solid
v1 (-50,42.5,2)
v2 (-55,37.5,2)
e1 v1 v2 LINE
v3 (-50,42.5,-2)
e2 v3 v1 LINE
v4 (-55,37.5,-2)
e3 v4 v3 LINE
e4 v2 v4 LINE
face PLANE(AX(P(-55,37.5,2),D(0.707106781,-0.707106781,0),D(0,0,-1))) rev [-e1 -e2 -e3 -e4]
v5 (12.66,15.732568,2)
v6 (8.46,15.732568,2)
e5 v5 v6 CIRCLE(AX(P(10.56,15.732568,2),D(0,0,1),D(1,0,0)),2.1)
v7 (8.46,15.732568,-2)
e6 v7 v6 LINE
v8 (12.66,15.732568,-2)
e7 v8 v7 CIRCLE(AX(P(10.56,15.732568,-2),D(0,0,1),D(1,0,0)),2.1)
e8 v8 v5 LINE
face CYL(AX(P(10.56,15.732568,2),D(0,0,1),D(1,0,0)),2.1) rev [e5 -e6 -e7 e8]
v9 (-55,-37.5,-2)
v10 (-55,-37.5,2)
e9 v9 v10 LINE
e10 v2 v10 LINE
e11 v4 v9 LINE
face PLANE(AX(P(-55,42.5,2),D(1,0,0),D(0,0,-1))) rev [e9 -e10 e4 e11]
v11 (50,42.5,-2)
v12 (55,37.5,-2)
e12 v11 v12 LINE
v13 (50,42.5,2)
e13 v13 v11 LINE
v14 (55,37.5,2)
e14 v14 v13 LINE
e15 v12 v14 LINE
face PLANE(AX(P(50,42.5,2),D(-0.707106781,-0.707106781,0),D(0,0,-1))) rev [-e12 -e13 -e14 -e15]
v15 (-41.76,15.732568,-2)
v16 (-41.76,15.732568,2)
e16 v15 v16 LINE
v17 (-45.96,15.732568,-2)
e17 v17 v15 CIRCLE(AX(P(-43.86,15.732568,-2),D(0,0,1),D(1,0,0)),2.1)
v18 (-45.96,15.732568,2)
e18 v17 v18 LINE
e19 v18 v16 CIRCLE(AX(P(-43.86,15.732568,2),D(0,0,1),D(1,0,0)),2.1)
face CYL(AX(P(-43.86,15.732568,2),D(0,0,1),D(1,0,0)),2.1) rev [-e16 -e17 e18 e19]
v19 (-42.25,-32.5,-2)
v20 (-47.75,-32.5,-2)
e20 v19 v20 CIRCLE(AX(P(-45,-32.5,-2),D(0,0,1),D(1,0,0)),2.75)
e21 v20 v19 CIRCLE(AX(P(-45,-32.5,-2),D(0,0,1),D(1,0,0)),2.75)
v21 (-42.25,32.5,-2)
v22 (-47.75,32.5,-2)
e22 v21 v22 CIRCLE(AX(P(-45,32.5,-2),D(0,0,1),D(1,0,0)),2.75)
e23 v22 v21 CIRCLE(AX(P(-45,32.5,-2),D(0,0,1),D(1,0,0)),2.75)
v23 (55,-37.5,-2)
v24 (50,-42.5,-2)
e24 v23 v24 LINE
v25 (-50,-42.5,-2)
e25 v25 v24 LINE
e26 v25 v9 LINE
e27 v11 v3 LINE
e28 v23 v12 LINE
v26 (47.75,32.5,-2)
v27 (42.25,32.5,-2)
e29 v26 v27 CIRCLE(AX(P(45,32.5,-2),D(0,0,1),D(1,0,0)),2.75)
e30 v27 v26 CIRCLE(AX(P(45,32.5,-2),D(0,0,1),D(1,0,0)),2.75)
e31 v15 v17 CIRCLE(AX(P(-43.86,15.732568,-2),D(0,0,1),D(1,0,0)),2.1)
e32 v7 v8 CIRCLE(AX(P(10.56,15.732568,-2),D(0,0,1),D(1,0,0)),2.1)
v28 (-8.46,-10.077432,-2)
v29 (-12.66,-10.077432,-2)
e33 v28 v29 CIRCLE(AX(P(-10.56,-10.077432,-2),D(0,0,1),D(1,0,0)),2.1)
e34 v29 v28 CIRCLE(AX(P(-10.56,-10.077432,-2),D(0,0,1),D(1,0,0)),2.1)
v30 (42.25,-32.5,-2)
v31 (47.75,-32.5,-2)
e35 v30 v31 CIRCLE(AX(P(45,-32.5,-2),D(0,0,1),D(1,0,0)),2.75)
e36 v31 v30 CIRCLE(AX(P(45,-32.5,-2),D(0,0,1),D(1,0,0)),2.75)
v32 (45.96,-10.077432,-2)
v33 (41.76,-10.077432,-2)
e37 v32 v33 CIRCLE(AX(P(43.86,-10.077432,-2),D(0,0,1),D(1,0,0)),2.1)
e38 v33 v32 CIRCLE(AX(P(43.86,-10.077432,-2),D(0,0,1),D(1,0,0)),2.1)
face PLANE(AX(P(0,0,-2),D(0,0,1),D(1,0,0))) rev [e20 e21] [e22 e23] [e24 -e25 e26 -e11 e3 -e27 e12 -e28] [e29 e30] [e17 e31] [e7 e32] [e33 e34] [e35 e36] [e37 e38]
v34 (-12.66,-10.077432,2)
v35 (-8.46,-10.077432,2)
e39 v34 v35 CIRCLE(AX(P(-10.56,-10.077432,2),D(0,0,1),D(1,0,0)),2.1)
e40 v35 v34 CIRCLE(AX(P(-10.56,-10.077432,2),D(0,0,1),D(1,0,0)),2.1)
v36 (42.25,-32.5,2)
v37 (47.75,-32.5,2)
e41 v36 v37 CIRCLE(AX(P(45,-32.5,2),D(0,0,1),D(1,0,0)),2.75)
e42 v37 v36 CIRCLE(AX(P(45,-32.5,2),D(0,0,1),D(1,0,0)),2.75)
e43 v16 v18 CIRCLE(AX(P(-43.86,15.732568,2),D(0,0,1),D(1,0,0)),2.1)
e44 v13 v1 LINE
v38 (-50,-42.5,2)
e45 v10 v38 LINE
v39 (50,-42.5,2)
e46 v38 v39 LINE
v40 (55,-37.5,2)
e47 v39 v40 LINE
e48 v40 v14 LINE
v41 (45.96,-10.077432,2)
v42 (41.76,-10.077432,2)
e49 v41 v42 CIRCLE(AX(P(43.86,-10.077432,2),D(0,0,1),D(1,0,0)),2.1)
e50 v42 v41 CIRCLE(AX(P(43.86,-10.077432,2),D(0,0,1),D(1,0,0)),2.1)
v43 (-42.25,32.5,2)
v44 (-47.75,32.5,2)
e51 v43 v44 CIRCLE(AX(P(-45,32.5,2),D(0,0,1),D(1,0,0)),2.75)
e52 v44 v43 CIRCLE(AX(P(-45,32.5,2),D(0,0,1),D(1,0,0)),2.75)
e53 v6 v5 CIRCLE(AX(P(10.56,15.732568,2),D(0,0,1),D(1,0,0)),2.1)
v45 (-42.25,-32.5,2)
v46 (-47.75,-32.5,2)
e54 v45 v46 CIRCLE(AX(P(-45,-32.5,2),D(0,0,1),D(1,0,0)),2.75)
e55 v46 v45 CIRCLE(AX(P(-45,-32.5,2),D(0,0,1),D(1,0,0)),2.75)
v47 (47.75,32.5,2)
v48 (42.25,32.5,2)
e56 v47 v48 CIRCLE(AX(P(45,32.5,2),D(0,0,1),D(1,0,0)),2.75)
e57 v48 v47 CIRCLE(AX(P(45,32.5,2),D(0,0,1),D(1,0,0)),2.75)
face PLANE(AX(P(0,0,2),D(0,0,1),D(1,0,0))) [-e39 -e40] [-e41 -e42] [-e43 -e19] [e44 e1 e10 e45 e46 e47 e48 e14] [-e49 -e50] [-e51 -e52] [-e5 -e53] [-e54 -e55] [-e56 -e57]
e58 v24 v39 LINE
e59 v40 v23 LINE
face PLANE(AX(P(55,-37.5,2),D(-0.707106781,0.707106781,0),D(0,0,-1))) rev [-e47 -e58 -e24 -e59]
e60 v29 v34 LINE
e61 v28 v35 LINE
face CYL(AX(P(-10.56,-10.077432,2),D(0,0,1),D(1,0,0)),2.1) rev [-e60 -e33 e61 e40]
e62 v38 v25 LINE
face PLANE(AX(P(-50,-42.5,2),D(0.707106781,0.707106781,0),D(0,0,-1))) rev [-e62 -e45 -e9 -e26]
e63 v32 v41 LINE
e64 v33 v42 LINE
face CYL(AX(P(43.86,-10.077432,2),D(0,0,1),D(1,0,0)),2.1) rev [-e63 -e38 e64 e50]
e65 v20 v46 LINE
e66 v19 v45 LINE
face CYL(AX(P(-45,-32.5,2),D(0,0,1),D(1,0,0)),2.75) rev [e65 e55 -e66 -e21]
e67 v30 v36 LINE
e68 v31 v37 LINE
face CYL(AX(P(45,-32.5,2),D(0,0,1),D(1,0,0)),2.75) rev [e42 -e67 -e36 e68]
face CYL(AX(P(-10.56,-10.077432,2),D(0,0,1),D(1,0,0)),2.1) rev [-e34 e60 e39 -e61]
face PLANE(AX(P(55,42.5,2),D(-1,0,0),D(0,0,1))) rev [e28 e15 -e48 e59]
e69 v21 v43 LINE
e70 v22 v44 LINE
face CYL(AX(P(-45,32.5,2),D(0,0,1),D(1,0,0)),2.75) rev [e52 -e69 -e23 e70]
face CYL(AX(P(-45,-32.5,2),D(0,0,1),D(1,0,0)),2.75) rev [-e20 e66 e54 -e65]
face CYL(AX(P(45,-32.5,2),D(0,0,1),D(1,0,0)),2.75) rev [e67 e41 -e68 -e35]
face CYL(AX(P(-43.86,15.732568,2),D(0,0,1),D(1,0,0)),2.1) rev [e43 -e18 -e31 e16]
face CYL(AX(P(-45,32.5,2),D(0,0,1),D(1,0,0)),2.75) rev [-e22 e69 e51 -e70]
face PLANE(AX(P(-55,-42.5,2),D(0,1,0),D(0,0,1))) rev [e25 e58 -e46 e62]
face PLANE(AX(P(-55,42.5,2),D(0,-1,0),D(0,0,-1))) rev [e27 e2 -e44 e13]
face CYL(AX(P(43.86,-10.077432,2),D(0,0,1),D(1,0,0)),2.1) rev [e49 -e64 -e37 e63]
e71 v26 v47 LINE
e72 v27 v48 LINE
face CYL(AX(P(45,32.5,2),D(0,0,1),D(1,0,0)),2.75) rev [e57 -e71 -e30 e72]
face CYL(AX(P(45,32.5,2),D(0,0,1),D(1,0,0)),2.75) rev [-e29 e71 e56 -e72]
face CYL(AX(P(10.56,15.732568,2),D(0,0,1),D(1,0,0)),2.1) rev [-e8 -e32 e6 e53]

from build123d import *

# Parameters (mm, degrees)
SKETCH_1_W                  = 110
SKETCH_1_H                  = 85
EXTRUDE_1_DEPTH             = 2
CHAMFER_1_SIZE              = 5
HOLE_WIZARD_5_5_5_5_1_D     = 5.5
HOLE_WIZARD_5_5_5_5_1_DEPTH = 15.61
HOLE_WIZARD_5_5_5_5_1_TIP   = 1.58771324
HOLE_WIZARD_M5_3_D          = 4.2


with BuildPart() as part:
    # 草图1 → 凸台-拉伸1 (new, symmetric)
    with BuildSketch(Plane.XY):
        Rectangle(SKETCH_1_W, SKETCH_1_H)
    extrude(amount=EXTRUDE_1_DEPTH, both=True)

    # 倒角1
    chamfer_1_edges = [part.edges().sort_by_distance(p)[0] for p in [
        (-55, 42.5, 0),
        (55, 42.5, 0),
        (55, -42.5, 0),
        (-55, -42.5, 0),
    ]]
    chamfer(chamfer_1_edges, length=CHAMFER_1_SIZE)

    # Ø5.5 (5.5) 直径孔1
    with Locations(Plane.XY.offset(2)):
        with Locations((45, 32.5), (45, -32.5), (-45, -32.5), (-45, 32.5)):
            Hole(HOLE_WIZARD_5_5_5_5_1_D / 2, depth=HOLE_WIZARD_5_5_5_5_1_DEPTH)
            with Locations((0, 0, -(HOLE_WIZARD_5_5_5_5_1_DEPTH + HOLE_WIZARD_5_5_5_5_1_TIP / 2))):  # 120° drill point
                Cone(0, HOLE_WIZARD_5_5_5_5_1_D / 2, HOLE_WIZARD_5_5_5_5_1_TIP, mode=Mode.SUBTRACT)

    # M5 螺纹孔3 (through all)
    with Locations(Plane.XY.offset(2)):
        with Locations((-43.86, 15.732567746), (10.56, 15.732567746), (-10.56, -10.077432254), (43.86, -10.077432254)):
            Hole(HOLE_WIZARD_M5_3_D / 2)


solid = part.part
